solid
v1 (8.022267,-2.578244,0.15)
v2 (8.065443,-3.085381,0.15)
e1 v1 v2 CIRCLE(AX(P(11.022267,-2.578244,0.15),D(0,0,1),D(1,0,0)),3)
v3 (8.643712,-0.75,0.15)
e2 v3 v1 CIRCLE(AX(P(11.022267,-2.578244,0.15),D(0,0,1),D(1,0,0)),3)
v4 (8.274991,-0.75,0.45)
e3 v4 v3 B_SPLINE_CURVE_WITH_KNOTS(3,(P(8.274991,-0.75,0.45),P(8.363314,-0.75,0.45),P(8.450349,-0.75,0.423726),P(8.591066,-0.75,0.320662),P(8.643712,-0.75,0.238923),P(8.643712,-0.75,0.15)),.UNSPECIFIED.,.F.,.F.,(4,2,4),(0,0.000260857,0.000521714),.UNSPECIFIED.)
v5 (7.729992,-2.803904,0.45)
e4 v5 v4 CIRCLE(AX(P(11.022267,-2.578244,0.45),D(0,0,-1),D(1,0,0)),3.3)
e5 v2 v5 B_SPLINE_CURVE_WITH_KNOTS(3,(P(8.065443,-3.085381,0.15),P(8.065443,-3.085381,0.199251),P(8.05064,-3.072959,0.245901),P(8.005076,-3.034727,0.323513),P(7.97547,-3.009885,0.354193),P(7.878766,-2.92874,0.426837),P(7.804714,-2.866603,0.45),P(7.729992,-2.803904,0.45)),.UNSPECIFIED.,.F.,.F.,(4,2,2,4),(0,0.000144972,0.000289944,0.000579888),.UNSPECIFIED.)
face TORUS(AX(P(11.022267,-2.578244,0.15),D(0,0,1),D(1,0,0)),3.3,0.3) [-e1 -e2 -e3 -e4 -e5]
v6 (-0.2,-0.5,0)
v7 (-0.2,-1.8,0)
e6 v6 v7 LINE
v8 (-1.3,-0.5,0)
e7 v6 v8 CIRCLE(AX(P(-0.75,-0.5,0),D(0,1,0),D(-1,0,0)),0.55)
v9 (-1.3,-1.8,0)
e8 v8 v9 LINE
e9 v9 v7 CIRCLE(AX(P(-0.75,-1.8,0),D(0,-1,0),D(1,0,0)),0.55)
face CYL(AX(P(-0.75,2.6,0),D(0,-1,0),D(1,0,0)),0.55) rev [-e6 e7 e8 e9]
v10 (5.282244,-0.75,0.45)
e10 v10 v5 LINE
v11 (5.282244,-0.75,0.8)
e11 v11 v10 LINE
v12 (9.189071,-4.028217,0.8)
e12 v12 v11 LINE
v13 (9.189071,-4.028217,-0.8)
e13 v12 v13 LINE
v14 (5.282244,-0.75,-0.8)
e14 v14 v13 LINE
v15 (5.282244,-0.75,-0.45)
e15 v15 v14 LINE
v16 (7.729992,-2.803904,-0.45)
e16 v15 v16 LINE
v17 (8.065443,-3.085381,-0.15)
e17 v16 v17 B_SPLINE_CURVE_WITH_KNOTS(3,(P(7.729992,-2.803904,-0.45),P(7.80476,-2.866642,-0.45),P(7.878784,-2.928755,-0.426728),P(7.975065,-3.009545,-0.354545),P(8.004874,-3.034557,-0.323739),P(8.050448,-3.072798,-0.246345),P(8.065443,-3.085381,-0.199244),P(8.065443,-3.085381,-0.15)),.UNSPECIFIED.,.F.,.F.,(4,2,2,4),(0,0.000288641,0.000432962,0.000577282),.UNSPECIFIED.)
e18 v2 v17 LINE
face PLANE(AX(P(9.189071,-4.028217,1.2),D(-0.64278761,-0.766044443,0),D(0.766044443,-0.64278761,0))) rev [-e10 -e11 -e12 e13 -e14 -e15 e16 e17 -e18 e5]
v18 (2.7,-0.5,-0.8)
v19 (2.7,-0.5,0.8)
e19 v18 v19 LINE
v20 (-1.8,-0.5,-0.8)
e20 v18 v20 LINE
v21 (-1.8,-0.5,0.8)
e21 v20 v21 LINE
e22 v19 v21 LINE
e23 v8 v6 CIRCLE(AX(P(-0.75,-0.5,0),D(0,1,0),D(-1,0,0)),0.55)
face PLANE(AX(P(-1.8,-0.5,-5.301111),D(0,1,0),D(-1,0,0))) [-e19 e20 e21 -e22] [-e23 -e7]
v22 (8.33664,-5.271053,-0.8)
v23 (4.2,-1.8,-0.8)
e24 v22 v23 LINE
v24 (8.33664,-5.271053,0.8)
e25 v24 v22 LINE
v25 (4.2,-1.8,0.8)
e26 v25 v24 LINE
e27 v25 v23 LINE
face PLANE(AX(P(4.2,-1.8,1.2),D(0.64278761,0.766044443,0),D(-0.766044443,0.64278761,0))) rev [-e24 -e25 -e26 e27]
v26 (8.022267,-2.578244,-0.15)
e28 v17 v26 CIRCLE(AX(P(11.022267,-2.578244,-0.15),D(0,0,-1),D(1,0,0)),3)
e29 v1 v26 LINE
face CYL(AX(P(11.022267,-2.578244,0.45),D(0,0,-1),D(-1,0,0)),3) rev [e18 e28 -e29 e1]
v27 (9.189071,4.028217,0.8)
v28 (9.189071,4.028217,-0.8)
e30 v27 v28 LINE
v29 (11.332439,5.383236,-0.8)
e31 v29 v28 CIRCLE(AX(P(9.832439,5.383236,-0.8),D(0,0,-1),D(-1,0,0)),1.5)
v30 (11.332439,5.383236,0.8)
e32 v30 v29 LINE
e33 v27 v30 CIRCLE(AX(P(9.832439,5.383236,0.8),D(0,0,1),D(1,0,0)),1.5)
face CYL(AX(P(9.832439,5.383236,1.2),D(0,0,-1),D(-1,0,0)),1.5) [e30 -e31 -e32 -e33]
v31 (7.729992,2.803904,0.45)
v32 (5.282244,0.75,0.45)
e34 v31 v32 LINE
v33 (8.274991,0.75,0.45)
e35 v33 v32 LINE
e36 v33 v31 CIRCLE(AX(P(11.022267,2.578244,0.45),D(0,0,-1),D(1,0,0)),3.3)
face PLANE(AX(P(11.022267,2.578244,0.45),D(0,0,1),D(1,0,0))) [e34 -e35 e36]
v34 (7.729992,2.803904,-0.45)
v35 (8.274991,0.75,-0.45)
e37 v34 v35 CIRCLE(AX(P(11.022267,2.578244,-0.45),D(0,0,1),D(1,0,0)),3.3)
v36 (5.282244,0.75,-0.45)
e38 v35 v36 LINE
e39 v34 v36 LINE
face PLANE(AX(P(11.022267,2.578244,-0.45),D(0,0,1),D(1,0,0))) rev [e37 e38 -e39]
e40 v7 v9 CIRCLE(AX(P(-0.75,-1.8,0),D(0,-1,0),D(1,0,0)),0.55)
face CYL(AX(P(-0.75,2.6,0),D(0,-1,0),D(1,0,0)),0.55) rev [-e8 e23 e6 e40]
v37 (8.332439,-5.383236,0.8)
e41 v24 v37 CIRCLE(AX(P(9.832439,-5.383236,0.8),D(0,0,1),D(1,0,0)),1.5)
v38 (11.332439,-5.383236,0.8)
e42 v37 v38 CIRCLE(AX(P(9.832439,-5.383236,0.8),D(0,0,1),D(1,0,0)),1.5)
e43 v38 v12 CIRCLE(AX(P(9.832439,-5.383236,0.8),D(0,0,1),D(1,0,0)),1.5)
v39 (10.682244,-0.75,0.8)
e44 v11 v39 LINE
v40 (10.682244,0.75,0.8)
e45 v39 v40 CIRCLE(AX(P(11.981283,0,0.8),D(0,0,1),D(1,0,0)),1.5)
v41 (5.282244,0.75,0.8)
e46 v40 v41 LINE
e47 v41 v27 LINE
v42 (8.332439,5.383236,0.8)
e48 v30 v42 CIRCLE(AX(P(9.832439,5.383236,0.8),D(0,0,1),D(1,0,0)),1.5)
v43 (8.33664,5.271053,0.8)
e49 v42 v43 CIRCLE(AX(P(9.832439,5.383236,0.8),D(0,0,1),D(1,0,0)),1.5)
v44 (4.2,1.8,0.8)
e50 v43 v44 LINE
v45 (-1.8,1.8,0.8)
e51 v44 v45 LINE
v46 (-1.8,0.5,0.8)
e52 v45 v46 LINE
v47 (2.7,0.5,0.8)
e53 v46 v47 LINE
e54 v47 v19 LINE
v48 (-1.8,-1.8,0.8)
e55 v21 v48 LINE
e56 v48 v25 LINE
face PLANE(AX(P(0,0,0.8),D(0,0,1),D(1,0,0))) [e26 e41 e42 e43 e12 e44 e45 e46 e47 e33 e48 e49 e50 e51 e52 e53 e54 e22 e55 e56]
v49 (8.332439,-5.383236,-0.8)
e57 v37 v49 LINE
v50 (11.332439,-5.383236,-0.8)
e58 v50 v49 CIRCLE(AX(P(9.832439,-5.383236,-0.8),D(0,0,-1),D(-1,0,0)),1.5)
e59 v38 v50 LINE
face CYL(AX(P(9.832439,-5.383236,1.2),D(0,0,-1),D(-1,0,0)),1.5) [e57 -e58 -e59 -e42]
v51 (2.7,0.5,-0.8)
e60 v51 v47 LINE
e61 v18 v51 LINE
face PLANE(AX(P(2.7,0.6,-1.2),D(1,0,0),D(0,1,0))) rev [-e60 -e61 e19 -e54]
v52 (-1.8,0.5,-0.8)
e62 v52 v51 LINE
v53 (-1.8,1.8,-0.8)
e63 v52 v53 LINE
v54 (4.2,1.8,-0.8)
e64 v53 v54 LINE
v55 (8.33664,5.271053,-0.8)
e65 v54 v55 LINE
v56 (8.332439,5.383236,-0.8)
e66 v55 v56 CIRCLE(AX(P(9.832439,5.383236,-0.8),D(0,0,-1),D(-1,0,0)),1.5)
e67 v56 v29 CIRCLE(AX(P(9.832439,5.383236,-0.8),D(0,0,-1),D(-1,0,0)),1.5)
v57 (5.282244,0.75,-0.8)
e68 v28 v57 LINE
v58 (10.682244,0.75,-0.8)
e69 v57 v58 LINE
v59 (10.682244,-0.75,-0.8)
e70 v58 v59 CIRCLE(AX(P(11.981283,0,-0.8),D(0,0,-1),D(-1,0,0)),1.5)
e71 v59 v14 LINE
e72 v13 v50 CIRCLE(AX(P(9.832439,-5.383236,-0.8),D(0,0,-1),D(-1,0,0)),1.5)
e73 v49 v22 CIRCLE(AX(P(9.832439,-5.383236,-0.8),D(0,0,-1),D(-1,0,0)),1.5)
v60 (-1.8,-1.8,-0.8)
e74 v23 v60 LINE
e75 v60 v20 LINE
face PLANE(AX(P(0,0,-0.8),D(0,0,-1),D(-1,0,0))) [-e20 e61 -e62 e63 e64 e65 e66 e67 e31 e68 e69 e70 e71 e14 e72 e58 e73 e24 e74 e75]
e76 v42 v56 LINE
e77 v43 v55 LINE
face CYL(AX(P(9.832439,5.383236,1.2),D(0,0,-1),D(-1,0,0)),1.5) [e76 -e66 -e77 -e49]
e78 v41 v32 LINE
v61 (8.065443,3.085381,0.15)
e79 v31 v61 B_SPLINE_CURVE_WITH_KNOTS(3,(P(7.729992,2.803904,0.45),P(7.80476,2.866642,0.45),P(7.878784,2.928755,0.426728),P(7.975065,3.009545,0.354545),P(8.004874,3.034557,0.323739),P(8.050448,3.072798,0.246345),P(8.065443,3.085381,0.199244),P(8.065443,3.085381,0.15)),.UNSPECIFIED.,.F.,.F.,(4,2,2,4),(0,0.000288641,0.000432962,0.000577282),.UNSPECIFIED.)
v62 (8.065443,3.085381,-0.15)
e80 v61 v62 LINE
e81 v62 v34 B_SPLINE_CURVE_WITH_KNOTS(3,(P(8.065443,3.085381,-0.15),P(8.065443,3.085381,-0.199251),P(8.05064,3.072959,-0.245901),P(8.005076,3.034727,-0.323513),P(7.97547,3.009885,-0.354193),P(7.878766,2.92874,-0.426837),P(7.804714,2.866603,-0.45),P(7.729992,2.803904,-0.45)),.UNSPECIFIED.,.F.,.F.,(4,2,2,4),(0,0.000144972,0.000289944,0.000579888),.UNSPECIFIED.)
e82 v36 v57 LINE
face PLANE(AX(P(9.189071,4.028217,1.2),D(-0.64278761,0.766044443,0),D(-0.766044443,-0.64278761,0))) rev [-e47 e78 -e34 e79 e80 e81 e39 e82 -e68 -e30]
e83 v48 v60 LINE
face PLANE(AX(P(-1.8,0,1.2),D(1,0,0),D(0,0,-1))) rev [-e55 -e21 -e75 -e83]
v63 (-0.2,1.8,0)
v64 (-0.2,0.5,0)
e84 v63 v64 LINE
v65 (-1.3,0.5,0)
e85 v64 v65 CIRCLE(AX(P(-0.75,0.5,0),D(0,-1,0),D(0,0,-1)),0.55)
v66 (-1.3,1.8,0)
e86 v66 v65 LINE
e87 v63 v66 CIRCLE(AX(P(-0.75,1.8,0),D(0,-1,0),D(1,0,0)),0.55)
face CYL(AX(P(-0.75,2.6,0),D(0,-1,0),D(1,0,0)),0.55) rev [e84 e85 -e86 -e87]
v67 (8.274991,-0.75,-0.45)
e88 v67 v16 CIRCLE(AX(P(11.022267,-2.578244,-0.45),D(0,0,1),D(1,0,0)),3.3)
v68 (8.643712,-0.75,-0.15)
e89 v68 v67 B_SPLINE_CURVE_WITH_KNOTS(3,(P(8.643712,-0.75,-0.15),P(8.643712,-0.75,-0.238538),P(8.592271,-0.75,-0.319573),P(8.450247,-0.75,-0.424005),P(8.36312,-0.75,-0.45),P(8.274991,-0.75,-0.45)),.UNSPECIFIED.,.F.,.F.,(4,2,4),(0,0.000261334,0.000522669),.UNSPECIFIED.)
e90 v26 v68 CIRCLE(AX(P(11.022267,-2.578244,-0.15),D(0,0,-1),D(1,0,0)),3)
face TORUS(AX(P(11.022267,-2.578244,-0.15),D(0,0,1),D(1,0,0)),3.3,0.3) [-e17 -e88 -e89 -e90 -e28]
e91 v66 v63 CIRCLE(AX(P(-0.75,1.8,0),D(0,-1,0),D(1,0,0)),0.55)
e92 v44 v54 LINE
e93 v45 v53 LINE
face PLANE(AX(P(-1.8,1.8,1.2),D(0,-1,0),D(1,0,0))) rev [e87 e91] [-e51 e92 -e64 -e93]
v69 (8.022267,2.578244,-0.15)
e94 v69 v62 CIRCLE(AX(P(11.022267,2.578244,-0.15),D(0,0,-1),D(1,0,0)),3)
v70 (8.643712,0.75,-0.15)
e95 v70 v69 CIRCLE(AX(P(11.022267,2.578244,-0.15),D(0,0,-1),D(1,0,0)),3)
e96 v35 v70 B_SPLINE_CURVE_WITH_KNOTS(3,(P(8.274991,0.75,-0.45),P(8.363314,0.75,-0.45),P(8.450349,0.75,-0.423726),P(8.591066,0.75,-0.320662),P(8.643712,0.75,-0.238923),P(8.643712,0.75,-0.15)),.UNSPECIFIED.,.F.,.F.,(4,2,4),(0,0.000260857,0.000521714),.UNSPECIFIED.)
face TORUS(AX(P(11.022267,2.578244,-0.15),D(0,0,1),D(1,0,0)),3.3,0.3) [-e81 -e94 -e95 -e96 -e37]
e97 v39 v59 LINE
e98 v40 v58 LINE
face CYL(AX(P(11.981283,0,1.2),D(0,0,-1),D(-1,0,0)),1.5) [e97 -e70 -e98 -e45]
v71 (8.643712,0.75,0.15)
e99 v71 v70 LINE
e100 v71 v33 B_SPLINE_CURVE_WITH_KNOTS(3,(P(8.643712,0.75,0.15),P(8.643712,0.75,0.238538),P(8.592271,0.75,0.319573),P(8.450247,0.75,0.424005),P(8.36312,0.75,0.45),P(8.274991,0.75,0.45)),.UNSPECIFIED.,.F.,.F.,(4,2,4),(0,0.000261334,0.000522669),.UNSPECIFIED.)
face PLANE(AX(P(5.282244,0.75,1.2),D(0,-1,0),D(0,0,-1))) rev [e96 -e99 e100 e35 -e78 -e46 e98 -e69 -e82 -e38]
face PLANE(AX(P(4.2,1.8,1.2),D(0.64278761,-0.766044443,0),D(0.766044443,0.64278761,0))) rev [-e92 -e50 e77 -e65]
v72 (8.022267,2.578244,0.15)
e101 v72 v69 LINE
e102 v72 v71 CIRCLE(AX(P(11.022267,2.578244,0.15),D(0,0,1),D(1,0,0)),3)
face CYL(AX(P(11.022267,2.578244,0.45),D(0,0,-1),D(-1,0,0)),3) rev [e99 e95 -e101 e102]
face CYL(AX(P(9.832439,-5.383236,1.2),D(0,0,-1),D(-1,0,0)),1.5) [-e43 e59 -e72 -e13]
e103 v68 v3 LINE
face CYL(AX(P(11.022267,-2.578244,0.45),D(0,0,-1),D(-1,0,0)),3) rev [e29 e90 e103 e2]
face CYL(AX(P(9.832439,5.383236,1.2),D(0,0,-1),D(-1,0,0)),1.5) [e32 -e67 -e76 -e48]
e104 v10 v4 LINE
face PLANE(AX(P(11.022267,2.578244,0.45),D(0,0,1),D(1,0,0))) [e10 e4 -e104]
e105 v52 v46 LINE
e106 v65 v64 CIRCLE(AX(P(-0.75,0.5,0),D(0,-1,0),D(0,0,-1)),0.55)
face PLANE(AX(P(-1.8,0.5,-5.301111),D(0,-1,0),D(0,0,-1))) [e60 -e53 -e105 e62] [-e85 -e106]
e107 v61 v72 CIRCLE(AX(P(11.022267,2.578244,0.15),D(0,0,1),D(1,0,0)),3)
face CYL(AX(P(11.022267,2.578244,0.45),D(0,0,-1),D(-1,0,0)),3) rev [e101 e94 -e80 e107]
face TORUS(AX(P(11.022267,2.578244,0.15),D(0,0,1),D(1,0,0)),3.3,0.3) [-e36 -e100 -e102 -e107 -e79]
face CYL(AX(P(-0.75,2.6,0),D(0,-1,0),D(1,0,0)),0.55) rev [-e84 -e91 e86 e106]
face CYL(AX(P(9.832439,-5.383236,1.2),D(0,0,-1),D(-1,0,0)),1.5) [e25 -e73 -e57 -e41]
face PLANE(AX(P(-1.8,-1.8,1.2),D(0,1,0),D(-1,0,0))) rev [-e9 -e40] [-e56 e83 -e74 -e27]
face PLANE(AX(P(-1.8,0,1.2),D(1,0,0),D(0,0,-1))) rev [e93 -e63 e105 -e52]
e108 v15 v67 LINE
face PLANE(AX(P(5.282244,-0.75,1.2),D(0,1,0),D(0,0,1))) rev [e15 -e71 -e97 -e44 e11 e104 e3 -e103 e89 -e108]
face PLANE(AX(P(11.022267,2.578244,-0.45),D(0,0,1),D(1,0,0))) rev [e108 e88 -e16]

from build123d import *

# Parameters (mm, degrees)
SALIENTE_EXTRUIR1_DEPTH = 4
SALIENTE_EXTRUIR2_DEPTH = 1.5
CROQUIS3_W              = 15
CROQUIS3_H              = 4
CORTAR_EXTRUIR1_DEPTH   = 52.086410566
CROQUIS4_R              = 1.65
CORTAR_EXTRUIR2_DEPTH   = 54.601779767
FILLET2_R               = 1
SCALE1_SCALE            = 0.3
SKETCH2_R               = 15.04592303
CUT_EXTRUDE3_DEPTH      = 0.4
SKETCH3_R               = 13.988720819
CUT_EXTRUDE4_DEPTH      = 0.4
SKETCH4_W               = 4.5
SKETCH4_H               = 0.1
BOSS_EXTRUDE1_DEPTH     = 1.6
SKETCH5_R               = 0.55
CUT_EXTRUDE5_DEPTH      = 4.4


with BuildPart() as part:
    # Sketch1 → Saliente-Extruir1 (new, symmetric)
    with BuildSketch(Plane.XY):
        with BuildLine():
            Line((-6, 0), (-6, 6))
            Line((-6, 6), (14, 6))
            Line((14, 6), (27.788799976, 17.570176974))
            ThreePointArc((27.788799976, 17.570176974), (36.898130887, 20.772215113), (30.630237093, 13.427389365))
            Line((30.630237093, 13.427389365), (17.60748156, 2.5))
            Line((17.60748156, 2.5), (35.60748156, 2.5))
            ThreePointArc((35.60748156, 2.5), (44.937608579, 0), (35.60748156, -2.5))
            Line((35.60748156, -2.5), (17.60748156, -2.5))
            Line((17.60748156, -2.5), (30.630237093, -13.427389365))
            ThreePointArc((30.630237093, -13.427389365), (36.898130887, -20.772215113), (27.788799976, -17.570176974))
            Line((27.788799976, -17.570176974), (14, -6))
            Line((14, -6), (-6, -6))
            Line((-6, -6), (-6, 0))
        make_face()
    extrude(amount=SALIENTE_EXTRUIR1_DEPTH, both=True)

    # Croquis2 → Saliente-Extruir2 (add, symmetric)
    with BuildSketch(Plane.XY):
        with BuildLine():
            Line((26.884808669, 10.284601755), (14.628097579, 0))
            Line((14.628097579, 0), (26.884808669, -10.284601755))
            ThreePointArc((26.884808669, -10.284601755), (27.660138353, -4.406075759), (31.628097579, 0))
            ThreePointArc((31.628097579, 0), (27.660138353, 4.406075759), (26.884808669, 10.284601755))
        make_face()
    extrude(amount=SALIENTE_EXTRUIR2_DEPTH, both=True)

    # Croquis3 → Cortar-Extruir1 (cut, through all)
    with BuildSketch(Plane.XY.offset(4)):
        with Locations((1.5, 0)):
            Rectangle(CROQUIS3_W, CROQUIS3_H)
    extrude(amount=-CORTAR_EXTRUIR1_DEPTH, mode=Mode.SUBTRACT)

    # Croquis4 → Cortar-Extruir2 (cut, through all)
    with BuildSketch(Plane(origin=(0, 6, 0), x_dir=(1, 0, 0), z_dir=(0, 1, 0))):
        with Locations(Location((-2.5, 0, 0), (0, 0, 180))):
            Circle(CROQUIS4_R)
    extrude(amount=-CORTAR_EXTRUIR2_DEPTH, mode=Mode.SUBTRACT)

    # Fillet2
    fillet2_edges = [part.edges().sort_by_distance(p)[0] for p in [
        (27.034037659, -6.190607199, -1.5),
        (27.034037659, 6.190607199, -1.5),
        (27.034037659, -6.190607199, 1.5),
        (27.034037659, 6.190607199, 1.5),
    ]]
    fillet(fillet2_edges, radius=FILLET2_R)


with BuildPart() as part_1:
    # Scale1: scaled about (0, 0, 0)
    add(part.part.scale(SCALE1_SCALE))

    # Sketch2 → Cut-Extrude3 (cut)
    with BuildSketch(Plane.XY.offset(1.2)):
        Circle(SKETCH2_R)
    extrude(amount=-CUT_EXTRUDE3_DEPTH, mode=Mode.SUBTRACT)

    # Sketch3 → Cut-Extrude4 (cut)
    with BuildSketch(Plane(origin=(0, 0, -1.2), x_dir=(-1, 0, 0), z_dir=(0, 0, -1))):
        Circle(SKETCH3_R)
    extrude(amount=-CUT_EXTRUDE4_DEPTH, mode=Mode.SUBTRACT)

    # Sketch4 → Boss-Extrude1 (add)
    with BuildSketch(Plane.XY.offset(0.8)):
        with Locations((0.45, -0.55)):
            Rectangle(SKETCH4_W, SKETCH4_H)
        with Locations((0.45, 0.55)):
            Rectangle(SKETCH4_W, SKETCH4_H)
    extrude(amount=-BOSS_EXTRUDE1_DEPTH)

    # Sketch5 → Cut-Extrude5 (cut)
    with BuildSketch(Plane.XZ.offset(1.8)):
        with Locations((-0.75, 0)):
            Circle(SKETCH5_R)
    extrude(amount=-CUT_EXTRUDE5_DEPTH, mode=Mode.SUBTRACT)


solid = part_1.part
